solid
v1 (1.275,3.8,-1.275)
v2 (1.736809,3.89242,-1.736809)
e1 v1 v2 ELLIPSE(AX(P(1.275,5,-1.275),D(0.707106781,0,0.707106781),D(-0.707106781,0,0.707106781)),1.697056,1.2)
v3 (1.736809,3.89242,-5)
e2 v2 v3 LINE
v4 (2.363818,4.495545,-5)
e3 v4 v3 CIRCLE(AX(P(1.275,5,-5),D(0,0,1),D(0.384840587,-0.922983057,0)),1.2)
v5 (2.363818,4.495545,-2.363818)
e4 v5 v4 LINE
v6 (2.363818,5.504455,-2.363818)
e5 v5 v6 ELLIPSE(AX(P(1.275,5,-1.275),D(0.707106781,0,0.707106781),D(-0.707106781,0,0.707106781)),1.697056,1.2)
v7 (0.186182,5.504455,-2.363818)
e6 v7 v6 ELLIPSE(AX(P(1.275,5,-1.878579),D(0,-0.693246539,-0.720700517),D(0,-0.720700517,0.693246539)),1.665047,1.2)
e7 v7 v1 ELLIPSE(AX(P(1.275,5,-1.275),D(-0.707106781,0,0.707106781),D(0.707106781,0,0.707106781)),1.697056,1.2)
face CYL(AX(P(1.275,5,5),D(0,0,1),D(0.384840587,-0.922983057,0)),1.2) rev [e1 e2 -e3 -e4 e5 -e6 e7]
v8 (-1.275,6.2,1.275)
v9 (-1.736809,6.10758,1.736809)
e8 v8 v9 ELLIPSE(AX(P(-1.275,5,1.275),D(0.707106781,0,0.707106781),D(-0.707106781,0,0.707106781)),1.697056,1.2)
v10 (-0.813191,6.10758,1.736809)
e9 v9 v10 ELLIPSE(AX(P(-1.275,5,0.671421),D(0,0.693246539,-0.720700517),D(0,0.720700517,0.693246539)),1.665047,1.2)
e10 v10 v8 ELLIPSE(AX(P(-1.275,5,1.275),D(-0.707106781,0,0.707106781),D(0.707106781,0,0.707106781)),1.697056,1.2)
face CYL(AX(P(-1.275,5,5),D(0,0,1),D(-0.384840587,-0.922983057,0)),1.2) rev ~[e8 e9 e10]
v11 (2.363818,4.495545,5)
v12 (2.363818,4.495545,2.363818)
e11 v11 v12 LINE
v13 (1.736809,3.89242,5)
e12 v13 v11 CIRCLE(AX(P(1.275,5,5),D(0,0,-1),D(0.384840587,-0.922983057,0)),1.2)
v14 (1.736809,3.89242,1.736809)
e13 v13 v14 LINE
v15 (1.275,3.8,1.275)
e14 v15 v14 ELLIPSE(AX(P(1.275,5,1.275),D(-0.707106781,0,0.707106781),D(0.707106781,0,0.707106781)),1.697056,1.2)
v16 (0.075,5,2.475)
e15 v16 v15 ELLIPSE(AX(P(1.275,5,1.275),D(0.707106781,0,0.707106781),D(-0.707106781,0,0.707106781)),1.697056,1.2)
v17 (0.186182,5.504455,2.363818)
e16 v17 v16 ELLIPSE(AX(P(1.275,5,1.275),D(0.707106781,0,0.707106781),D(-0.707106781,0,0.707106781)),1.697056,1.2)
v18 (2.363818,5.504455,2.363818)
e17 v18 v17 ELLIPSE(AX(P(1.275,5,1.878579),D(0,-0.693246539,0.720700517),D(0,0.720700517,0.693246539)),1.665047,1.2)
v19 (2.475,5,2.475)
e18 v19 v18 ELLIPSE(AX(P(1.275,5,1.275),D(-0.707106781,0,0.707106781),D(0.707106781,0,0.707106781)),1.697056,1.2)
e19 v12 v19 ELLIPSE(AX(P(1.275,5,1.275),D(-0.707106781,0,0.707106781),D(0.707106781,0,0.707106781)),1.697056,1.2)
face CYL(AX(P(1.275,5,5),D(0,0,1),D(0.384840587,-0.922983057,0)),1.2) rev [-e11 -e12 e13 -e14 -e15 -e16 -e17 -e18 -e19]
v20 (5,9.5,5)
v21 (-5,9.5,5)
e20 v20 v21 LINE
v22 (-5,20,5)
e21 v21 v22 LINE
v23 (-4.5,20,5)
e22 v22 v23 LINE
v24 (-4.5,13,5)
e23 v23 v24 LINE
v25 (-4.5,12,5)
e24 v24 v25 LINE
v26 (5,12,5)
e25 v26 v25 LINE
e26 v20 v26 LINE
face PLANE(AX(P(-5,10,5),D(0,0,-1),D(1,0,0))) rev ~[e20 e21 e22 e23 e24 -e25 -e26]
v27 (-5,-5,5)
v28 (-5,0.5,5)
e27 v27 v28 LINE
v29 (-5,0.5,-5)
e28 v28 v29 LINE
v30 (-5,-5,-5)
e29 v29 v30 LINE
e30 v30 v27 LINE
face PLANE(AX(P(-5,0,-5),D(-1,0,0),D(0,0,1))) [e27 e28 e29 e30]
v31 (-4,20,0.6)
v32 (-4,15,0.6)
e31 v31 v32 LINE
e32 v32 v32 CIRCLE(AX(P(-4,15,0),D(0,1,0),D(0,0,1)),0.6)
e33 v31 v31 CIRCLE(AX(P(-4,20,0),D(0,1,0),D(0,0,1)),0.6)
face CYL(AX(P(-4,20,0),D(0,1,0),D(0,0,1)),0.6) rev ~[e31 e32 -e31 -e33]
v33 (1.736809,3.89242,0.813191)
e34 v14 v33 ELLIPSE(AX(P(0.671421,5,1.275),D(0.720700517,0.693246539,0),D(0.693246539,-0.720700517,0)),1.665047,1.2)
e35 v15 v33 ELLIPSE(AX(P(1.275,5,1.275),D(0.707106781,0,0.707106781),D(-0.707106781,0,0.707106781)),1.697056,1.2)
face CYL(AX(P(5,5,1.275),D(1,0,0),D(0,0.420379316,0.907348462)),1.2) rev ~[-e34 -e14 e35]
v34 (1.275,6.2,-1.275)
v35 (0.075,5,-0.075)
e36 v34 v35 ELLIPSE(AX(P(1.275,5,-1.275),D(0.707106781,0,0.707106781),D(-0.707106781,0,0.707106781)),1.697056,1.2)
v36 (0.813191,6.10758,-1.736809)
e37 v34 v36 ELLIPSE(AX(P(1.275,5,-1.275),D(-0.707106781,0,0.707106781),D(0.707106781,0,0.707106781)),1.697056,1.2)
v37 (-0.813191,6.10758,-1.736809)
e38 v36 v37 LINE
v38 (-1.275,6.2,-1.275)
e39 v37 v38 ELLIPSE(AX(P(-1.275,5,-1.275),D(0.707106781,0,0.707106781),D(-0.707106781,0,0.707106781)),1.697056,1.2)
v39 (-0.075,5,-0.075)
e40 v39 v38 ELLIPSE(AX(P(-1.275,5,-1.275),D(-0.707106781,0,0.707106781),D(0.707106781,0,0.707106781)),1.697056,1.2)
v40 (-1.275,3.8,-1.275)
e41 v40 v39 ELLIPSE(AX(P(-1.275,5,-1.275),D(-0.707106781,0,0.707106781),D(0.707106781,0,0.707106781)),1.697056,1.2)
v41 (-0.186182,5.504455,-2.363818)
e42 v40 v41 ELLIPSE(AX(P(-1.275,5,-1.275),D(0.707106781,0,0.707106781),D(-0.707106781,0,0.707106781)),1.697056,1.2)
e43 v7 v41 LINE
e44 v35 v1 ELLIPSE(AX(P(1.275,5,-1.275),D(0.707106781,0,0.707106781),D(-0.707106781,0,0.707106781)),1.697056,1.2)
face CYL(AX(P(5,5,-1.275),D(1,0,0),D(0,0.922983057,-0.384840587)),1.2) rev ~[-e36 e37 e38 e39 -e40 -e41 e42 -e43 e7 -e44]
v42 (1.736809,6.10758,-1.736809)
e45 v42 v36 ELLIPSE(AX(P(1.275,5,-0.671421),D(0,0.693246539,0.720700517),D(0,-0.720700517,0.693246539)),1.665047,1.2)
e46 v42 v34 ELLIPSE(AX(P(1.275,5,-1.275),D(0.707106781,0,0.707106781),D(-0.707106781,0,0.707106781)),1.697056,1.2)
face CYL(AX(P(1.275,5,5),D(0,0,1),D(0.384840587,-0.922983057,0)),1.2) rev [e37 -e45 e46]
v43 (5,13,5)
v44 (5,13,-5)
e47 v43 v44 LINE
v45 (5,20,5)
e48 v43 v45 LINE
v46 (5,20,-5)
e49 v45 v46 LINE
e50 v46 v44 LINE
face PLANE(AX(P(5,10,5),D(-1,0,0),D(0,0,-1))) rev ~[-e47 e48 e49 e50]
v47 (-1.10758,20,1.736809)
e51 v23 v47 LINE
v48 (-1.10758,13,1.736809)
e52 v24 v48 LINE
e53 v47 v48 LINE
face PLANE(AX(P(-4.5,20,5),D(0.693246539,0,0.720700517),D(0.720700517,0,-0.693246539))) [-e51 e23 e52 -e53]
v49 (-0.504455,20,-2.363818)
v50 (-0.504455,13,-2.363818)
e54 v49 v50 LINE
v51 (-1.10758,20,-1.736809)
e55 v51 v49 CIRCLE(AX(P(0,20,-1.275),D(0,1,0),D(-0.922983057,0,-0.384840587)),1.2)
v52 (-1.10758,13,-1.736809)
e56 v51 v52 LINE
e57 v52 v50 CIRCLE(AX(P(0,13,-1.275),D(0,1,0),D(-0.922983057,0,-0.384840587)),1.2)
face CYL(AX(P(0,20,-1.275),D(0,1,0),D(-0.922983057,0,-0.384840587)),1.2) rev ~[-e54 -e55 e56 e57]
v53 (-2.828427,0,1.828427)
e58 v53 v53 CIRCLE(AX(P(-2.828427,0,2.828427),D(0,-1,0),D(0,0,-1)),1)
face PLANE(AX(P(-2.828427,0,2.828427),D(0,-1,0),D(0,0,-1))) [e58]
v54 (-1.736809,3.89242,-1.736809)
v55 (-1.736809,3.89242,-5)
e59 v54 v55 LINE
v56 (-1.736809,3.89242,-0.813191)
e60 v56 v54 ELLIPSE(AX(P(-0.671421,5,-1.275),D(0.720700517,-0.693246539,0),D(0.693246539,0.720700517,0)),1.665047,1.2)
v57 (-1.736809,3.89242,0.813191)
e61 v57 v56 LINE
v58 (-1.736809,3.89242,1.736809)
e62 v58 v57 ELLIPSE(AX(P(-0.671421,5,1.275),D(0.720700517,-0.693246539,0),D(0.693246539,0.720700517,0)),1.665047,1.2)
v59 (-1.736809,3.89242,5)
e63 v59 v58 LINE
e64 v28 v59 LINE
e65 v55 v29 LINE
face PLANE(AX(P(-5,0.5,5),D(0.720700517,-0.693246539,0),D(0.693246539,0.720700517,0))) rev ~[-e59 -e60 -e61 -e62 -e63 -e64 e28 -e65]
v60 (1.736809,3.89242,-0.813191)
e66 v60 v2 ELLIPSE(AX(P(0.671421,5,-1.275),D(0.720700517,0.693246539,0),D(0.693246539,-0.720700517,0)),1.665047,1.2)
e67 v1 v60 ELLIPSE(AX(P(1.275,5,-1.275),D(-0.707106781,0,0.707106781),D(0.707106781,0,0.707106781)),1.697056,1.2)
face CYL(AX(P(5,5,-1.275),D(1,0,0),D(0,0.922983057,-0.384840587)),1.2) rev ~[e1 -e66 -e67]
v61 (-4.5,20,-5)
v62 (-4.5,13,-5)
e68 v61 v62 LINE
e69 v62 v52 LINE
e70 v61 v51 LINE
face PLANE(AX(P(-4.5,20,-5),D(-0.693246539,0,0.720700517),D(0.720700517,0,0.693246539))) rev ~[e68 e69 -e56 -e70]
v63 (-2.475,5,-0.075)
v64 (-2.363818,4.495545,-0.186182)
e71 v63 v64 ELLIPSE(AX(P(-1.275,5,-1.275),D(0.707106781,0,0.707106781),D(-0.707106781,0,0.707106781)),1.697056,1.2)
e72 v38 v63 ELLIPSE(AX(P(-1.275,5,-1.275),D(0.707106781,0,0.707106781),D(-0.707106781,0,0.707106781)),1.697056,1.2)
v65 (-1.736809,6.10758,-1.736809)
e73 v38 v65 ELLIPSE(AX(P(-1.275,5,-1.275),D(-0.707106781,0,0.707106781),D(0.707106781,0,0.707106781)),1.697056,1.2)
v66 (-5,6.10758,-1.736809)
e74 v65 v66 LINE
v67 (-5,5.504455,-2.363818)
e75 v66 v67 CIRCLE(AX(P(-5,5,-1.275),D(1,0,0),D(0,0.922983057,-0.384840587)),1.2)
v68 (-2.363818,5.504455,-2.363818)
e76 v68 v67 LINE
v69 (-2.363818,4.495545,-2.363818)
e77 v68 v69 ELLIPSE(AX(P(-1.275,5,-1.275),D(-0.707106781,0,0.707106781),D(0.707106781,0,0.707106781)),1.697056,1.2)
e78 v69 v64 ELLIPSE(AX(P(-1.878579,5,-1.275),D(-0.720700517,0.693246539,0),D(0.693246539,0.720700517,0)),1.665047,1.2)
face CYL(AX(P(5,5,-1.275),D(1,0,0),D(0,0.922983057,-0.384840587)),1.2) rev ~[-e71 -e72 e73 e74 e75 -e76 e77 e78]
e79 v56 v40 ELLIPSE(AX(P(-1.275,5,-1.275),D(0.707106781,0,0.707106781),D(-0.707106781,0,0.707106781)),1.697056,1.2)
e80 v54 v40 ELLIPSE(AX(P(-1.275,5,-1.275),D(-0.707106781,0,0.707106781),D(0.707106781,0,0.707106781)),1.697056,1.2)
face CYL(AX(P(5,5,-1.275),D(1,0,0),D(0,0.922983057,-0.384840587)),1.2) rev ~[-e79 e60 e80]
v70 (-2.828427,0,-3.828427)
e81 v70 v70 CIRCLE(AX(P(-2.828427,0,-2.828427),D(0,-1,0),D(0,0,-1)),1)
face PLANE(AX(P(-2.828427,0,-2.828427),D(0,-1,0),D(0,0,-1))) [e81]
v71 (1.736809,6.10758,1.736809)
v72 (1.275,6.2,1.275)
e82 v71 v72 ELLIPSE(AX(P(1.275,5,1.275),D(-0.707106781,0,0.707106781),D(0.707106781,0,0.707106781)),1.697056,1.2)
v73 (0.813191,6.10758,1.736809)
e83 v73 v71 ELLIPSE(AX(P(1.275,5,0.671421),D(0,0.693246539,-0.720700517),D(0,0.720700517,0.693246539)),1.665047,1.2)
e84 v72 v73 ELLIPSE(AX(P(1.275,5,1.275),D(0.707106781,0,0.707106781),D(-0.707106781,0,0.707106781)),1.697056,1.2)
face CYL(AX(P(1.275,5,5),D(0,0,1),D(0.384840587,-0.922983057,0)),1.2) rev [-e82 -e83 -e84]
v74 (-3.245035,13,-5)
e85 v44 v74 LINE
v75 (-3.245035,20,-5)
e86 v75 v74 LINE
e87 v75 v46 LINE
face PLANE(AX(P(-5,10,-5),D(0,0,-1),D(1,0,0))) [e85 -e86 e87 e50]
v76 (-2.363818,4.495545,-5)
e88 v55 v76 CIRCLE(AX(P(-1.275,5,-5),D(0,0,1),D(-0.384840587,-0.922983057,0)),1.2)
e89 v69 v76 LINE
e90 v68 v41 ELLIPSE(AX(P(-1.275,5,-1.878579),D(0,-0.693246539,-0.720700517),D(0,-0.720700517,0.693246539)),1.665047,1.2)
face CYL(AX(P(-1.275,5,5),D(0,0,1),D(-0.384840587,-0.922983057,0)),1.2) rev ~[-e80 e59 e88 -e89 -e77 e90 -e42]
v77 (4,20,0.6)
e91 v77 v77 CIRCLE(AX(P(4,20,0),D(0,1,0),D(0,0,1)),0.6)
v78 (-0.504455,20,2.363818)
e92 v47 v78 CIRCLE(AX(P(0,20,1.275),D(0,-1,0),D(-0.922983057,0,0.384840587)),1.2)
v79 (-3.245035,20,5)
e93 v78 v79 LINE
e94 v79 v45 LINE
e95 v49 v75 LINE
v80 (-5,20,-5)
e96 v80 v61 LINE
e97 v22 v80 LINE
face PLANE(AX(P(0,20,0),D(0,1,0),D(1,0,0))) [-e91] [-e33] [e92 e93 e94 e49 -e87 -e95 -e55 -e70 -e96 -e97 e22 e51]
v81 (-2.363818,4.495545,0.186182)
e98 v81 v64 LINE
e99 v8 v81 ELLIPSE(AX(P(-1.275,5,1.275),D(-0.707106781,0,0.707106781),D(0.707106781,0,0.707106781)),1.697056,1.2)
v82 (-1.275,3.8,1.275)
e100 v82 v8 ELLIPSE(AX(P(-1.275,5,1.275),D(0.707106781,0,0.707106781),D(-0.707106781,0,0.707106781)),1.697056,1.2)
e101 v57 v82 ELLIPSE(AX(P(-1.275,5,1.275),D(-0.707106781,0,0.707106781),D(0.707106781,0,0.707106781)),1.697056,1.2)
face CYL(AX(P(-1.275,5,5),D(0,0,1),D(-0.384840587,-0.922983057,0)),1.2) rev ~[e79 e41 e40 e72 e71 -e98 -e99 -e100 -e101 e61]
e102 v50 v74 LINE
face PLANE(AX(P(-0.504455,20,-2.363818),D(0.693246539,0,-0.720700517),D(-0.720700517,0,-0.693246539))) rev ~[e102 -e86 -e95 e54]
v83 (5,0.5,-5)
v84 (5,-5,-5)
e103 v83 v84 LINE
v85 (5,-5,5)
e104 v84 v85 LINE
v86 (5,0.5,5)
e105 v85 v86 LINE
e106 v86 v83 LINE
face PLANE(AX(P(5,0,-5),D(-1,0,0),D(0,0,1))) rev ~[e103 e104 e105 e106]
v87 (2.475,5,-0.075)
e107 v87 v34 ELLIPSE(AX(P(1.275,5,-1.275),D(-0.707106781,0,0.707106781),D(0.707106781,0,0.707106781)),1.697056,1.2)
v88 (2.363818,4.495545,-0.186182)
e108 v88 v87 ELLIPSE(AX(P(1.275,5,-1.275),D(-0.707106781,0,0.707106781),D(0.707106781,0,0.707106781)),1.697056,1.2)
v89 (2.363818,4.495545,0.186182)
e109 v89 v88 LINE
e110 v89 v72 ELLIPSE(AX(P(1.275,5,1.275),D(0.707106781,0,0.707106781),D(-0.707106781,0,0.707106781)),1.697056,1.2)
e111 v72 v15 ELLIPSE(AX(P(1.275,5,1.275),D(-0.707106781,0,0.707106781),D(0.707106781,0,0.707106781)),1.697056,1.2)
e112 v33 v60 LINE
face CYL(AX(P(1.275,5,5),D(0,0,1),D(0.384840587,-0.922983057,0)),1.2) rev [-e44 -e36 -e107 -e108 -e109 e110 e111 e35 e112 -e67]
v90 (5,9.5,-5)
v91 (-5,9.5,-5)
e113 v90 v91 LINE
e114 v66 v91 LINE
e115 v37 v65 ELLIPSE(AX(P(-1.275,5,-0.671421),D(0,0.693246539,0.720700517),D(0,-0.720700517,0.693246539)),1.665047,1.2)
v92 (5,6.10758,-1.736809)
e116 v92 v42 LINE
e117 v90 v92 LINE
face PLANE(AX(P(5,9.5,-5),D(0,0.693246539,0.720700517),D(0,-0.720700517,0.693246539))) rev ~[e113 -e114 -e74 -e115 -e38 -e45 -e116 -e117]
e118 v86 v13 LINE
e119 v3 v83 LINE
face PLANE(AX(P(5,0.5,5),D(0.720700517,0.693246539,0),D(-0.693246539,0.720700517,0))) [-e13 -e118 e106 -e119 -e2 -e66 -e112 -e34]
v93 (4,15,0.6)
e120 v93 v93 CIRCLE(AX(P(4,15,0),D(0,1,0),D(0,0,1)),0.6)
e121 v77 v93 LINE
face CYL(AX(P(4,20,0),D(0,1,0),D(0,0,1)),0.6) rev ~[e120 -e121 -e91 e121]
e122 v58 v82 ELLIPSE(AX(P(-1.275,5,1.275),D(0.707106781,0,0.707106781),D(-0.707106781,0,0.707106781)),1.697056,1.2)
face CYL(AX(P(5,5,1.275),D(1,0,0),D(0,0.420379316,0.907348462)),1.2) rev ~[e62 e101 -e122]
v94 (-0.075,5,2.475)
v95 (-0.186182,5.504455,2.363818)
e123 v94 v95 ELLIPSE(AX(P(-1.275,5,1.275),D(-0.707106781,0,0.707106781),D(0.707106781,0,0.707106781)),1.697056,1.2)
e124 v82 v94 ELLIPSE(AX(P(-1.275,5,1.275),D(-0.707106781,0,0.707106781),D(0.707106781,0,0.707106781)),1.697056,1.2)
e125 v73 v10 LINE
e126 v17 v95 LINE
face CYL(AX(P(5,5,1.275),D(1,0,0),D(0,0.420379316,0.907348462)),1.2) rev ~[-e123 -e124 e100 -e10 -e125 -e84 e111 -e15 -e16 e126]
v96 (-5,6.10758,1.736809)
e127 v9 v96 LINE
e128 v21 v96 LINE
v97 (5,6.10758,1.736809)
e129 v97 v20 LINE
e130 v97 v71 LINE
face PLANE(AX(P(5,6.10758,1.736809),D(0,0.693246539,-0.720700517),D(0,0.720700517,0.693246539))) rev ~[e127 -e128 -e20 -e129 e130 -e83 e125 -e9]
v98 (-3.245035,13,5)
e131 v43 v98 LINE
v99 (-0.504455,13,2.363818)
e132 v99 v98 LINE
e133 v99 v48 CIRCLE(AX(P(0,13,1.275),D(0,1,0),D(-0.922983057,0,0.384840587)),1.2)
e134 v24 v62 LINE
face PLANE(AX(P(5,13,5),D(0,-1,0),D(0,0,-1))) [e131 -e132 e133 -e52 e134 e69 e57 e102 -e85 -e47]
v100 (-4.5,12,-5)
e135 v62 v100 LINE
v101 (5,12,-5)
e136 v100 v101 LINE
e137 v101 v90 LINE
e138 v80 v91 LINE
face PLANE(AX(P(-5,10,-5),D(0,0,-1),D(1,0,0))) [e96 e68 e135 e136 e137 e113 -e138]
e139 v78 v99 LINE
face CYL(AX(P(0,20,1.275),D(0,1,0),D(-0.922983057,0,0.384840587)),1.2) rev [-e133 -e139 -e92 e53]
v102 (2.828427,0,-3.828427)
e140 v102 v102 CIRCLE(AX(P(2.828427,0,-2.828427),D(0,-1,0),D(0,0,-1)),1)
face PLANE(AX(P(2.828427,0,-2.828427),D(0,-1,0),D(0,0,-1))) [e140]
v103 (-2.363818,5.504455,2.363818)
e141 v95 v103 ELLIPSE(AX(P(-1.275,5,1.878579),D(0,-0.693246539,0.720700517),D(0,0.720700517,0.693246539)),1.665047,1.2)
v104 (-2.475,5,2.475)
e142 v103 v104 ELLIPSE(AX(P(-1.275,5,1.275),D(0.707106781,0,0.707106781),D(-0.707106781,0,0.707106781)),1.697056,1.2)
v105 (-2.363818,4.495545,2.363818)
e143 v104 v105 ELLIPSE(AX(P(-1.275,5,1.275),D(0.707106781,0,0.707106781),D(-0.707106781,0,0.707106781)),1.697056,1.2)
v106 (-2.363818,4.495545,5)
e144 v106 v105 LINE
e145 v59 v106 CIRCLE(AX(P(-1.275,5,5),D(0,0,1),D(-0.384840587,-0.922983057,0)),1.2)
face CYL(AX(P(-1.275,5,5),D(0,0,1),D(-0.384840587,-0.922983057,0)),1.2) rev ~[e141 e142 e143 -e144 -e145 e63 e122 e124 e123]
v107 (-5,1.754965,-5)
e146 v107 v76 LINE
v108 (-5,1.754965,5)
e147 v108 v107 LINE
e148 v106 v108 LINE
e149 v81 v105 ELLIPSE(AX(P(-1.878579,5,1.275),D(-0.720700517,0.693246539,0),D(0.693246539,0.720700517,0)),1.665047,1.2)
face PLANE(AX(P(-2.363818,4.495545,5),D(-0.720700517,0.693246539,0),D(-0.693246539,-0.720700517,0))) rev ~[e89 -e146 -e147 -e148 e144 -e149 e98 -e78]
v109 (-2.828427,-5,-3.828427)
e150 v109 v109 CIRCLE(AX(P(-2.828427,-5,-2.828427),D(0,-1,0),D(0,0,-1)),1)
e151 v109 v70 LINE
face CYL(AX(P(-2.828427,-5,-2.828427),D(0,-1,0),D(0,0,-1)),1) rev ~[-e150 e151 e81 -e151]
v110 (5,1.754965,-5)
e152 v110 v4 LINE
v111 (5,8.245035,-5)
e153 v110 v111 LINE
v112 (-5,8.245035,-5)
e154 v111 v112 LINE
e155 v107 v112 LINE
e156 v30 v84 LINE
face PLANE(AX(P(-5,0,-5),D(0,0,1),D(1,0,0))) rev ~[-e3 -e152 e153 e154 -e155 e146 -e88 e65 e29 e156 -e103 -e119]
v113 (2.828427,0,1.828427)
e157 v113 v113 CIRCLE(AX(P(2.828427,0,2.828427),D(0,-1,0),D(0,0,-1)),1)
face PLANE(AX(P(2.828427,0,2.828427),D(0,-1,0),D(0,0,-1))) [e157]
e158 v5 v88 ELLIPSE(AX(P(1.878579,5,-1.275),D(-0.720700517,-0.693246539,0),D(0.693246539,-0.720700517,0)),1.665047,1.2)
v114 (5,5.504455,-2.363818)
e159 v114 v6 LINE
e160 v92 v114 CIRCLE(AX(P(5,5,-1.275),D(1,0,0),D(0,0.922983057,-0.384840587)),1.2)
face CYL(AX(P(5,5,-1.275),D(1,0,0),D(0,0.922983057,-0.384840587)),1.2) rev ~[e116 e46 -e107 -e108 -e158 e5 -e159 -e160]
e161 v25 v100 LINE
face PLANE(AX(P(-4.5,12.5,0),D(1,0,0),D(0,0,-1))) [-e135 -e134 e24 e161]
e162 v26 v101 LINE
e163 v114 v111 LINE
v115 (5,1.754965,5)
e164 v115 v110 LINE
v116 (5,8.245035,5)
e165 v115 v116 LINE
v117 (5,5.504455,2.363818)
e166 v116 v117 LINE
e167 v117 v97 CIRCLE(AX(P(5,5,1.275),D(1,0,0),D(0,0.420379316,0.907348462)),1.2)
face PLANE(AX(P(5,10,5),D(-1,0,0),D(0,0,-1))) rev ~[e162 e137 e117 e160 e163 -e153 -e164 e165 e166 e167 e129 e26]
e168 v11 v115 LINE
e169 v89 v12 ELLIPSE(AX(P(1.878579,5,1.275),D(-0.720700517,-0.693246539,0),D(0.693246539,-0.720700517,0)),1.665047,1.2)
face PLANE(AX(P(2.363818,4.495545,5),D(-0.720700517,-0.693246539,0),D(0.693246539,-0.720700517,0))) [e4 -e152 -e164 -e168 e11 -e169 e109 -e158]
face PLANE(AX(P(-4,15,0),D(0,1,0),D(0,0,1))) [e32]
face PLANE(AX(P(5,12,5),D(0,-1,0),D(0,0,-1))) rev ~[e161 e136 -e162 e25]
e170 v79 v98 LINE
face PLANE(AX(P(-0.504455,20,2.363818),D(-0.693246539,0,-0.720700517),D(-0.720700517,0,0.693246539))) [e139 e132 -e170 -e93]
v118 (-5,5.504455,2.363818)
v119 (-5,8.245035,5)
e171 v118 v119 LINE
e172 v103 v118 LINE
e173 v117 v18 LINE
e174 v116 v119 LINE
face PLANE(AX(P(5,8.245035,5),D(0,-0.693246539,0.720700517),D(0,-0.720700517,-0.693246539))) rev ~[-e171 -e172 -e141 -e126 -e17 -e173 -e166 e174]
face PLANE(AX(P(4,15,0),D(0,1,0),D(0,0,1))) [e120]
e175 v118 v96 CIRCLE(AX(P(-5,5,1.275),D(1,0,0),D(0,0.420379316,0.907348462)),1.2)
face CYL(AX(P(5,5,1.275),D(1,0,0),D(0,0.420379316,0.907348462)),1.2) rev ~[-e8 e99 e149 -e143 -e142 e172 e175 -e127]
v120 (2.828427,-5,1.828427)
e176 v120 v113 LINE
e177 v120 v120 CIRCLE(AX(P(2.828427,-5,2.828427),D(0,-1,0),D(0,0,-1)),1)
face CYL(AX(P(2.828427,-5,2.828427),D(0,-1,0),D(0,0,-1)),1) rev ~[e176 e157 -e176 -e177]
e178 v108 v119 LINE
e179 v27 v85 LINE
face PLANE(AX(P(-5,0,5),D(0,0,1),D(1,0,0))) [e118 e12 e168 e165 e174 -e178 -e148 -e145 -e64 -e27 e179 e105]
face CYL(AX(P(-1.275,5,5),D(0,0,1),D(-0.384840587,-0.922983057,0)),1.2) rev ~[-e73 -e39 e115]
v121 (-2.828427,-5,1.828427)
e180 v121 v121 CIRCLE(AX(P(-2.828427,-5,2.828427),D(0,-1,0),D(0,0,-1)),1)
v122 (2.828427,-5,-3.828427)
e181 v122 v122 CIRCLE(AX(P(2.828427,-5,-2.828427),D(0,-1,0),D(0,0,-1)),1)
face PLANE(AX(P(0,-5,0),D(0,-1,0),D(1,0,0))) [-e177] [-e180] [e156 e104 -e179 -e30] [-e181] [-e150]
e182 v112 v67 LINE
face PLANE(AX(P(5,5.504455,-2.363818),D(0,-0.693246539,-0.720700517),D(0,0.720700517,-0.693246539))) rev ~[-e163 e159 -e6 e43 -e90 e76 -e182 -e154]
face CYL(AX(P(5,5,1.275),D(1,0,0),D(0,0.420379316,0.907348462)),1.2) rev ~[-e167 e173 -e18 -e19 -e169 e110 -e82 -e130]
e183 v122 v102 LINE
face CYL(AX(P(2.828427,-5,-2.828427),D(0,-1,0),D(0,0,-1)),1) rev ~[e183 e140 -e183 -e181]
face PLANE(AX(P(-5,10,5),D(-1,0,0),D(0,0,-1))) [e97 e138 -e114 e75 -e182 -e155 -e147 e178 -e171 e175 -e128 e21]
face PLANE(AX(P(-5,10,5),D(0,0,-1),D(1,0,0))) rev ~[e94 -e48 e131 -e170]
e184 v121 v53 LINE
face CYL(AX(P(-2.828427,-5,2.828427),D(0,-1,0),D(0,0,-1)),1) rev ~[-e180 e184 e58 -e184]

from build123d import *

# Parameters (mm, degrees)
SKETCH1_W           = 10
SKETCH1_H           = 10
BOSS_EXTRUDE1_DEPTH = 10
CUT_EXTRUDE1_DEPTH  = 16
CUT_EXTRUDE2_DEPTH  = 16
SKETCH4_W           = 10
SKETCH4_H           = 10
BOSS_EXTRUDE2_DEPTH = 5
SKETCH5_W           = 10
SKETCH5_H           = 10
BOSS_EXTRUDE3_DEPTH = 10
CUT_EXTRUDE3_DEPTH  = 8
SKETCH8_W           = 10
SKETCH8_H           = 1
CUT_EXTRUDE4_DEPTH  = 9.5
SKETCH10_R          = 1
CUT_EXTRUDE5_DEPTH  = 5
SKETCH11_R          = 0.6
CUT_EXTRUDE6_DEPTH  = 5


with BuildPart() as part:
    # Sketch1 → Boss-Extrude1 (new body)
    with BuildSketch(Plane(origin=(0, 0, 0), x_dir=(1, 0, 0), z_dir=(0, 1, 0))):
        Rectangle(SKETCH1_W, SKETCH1_H)
    extrude(amount=BOSS_EXTRUDE1_DEPTH)

    # Sketch2 → Cut-Extrude1 (cut, through all)
    with BuildSketch(Plane.XY.offset(5)):
        with BuildLine():
            Line((2.363818154, 4.495544821), (5, 1.754964793))
            Line((5, 1.754964793), (5, 0.5))
            Line((5, 0.5), (1.736808704, 3.892420332))
            ThreePointArc((1.736808704, 3.892420332), (0.443104153, 5.864840621), (2.363818154, 4.495544821))
        make_face()
        with BuildLine():
            Line((-5, 1.754964793), (-5, 0.5))
            Line((-5, 0.5), (-1.736808704, 3.892420332))
            ThreePointArc((-1.736808704, 3.892420332), (-0.443104153, 5.864840621), (-2.363818154, 4.495544821))
            Line((-2.363818154, 4.495544821), (-5, 1.754964793))
        make_face()
    extrude(amount=-CUT_EXTRUDE1_DEPTH, mode=Mode.SUBTRACT)

    # Sketch3 → Cut-Extrude2 (cut, through all)
    with BuildSketch(Plane(origin=(5, 0, 0), x_dir=(0, 0, -1), z_dir=(1, 0, 0))):
        with BuildLine():
            Line((2.363818154, 5.504455179), (5, 8.245035207))
            Line((5, 8.245035207), (5, 9.5))
            Line((5, 9.5), (1.736808704, 6.107579668))
            ThreePointArc((1.736808704, 6.107579668), (0.443104153, 4.135159379), (2.363818154, 5.504455179))
        make_face()
        with BuildLine():
            Line((-5, 9.5), (-5, 8.245035207))
            Line((-5, 8.245035207), (-2.363818154, 5.504455179))
            ThreePointArc((-2.363818154, 5.504455179), (-0.443104153, 4.135159379), (-1.736808704, 6.107579668))
            Line((-1.736808704, 6.107579668), (-5, 9.5))
        make_face()
    extrude(amount=-CUT_EXTRUDE2_DEPTH, mode=Mode.SUBTRACT)

    # Sketch4 → Boss-Extrude2 (add)
    with BuildSketch(Plane.XZ):
        Rectangle(SKETCH4_W, SKETCH4_H)
    extrude(amount=BOSS_EXTRUDE2_DEPTH)

    # Sketch5 → Boss-Extrude3 (add)
    with BuildSketch(Plane(origin=(0, 10, 0), x_dir=(1, 0, 0), z_dir=(0, 1, 0))):
        Rectangle(SKETCH5_W, SKETCH5_H)
    extrude(amount=BOSS_EXTRUDE3_DEPTH)

    # Sketch7 → Cut-Extrude3 (cut)
    with BuildSketch(Plane(origin=(0, 20, 0), x_dir=(1, 0, 0), z_dir=(0, 1, 0))):
        with BuildLine():
            Line((-0.504455179, -2.363818154), (-3.245035207, -5))
            Line((-3.245035207, -5), (-4.5, -5))
            Line((-4.5, -5), (-1.107579668, -1.736808704))
            ThreePointArc((-1.107579668, -1.736808704), (0.864840621, -0.443104153), (-0.504455179, -2.363818154))
        make_face()
        with BuildLine():
            Line((-3.245035207, 5), (-4.5, 5))
            Line((-4.5, 5), (-1.107579668, 1.736808704))
            ThreePointArc((-1.107579668, 1.736808704), (0.864840621, 0.443104153), (-0.504455179, 2.363818154))
            Line((-0.504455179, 2.363818154), (-3.245035207, 5))
        make_face()
    extrude(amount=-CUT_EXTRUDE3_DEPTH, mode=Mode.SUBTRACT)

    # Sketch8 → Cut-Extrude4 (cut)
    with BuildSketch(Plane(origin=(5, 0, 0), x_dir=(0, 0, -1), z_dir=(1, 0, 0))):
        with Locations((0, 12.5)):
            Rectangle(SKETCH8_W, SKETCH8_H)
    extrude(amount=-CUT_EXTRUDE4_DEPTH, mode=Mode.SUBTRACT)

    # Sketch10 → Cut-Extrude5 (cut)
    with BuildSketch(Plane.XZ.offset(5)):
        with Locations(Location((-2.828427125, 2.828427125, 0), (0, 0, 270))):
            Circle(SKETCH10_R)
        with Locations(Location((2.828427125, 2.828427125, 0), (0, 0, 270))):
            Circle(SKETCH10_R)
        with Locations(Location((2.828427125, -2.828427125, 0), (0, 0, 270))):
            Circle(SKETCH10_R)
        with Locations(Location((-2.828427125, -2.828427125, 0), (0, 0, 270))):
            Circle(SKETCH10_R)
    extrude(amount=-CUT_EXTRUDE5_DEPTH, mode=Mode.SUBTRACT)

    # Sketch11 → Cut-Extrude6 (cut)
    with BuildSketch(Plane(origin=(0, 20, 0), x_dir=(1, 0, 0), z_dir=(0, 1, 0))):
        with Locations(Location((4, 0, 0), (0, 0, 270))):
            Circle(SKETCH11_R)
        with Locations(Location((-4, 0, 0), (0, 0, 270))):
            Circle(SKETCH11_R)
    extrude(amount=-CUT_EXTRUDE6_DEPTH, mode=Mode.SUBTRACT)


solid = part.part
